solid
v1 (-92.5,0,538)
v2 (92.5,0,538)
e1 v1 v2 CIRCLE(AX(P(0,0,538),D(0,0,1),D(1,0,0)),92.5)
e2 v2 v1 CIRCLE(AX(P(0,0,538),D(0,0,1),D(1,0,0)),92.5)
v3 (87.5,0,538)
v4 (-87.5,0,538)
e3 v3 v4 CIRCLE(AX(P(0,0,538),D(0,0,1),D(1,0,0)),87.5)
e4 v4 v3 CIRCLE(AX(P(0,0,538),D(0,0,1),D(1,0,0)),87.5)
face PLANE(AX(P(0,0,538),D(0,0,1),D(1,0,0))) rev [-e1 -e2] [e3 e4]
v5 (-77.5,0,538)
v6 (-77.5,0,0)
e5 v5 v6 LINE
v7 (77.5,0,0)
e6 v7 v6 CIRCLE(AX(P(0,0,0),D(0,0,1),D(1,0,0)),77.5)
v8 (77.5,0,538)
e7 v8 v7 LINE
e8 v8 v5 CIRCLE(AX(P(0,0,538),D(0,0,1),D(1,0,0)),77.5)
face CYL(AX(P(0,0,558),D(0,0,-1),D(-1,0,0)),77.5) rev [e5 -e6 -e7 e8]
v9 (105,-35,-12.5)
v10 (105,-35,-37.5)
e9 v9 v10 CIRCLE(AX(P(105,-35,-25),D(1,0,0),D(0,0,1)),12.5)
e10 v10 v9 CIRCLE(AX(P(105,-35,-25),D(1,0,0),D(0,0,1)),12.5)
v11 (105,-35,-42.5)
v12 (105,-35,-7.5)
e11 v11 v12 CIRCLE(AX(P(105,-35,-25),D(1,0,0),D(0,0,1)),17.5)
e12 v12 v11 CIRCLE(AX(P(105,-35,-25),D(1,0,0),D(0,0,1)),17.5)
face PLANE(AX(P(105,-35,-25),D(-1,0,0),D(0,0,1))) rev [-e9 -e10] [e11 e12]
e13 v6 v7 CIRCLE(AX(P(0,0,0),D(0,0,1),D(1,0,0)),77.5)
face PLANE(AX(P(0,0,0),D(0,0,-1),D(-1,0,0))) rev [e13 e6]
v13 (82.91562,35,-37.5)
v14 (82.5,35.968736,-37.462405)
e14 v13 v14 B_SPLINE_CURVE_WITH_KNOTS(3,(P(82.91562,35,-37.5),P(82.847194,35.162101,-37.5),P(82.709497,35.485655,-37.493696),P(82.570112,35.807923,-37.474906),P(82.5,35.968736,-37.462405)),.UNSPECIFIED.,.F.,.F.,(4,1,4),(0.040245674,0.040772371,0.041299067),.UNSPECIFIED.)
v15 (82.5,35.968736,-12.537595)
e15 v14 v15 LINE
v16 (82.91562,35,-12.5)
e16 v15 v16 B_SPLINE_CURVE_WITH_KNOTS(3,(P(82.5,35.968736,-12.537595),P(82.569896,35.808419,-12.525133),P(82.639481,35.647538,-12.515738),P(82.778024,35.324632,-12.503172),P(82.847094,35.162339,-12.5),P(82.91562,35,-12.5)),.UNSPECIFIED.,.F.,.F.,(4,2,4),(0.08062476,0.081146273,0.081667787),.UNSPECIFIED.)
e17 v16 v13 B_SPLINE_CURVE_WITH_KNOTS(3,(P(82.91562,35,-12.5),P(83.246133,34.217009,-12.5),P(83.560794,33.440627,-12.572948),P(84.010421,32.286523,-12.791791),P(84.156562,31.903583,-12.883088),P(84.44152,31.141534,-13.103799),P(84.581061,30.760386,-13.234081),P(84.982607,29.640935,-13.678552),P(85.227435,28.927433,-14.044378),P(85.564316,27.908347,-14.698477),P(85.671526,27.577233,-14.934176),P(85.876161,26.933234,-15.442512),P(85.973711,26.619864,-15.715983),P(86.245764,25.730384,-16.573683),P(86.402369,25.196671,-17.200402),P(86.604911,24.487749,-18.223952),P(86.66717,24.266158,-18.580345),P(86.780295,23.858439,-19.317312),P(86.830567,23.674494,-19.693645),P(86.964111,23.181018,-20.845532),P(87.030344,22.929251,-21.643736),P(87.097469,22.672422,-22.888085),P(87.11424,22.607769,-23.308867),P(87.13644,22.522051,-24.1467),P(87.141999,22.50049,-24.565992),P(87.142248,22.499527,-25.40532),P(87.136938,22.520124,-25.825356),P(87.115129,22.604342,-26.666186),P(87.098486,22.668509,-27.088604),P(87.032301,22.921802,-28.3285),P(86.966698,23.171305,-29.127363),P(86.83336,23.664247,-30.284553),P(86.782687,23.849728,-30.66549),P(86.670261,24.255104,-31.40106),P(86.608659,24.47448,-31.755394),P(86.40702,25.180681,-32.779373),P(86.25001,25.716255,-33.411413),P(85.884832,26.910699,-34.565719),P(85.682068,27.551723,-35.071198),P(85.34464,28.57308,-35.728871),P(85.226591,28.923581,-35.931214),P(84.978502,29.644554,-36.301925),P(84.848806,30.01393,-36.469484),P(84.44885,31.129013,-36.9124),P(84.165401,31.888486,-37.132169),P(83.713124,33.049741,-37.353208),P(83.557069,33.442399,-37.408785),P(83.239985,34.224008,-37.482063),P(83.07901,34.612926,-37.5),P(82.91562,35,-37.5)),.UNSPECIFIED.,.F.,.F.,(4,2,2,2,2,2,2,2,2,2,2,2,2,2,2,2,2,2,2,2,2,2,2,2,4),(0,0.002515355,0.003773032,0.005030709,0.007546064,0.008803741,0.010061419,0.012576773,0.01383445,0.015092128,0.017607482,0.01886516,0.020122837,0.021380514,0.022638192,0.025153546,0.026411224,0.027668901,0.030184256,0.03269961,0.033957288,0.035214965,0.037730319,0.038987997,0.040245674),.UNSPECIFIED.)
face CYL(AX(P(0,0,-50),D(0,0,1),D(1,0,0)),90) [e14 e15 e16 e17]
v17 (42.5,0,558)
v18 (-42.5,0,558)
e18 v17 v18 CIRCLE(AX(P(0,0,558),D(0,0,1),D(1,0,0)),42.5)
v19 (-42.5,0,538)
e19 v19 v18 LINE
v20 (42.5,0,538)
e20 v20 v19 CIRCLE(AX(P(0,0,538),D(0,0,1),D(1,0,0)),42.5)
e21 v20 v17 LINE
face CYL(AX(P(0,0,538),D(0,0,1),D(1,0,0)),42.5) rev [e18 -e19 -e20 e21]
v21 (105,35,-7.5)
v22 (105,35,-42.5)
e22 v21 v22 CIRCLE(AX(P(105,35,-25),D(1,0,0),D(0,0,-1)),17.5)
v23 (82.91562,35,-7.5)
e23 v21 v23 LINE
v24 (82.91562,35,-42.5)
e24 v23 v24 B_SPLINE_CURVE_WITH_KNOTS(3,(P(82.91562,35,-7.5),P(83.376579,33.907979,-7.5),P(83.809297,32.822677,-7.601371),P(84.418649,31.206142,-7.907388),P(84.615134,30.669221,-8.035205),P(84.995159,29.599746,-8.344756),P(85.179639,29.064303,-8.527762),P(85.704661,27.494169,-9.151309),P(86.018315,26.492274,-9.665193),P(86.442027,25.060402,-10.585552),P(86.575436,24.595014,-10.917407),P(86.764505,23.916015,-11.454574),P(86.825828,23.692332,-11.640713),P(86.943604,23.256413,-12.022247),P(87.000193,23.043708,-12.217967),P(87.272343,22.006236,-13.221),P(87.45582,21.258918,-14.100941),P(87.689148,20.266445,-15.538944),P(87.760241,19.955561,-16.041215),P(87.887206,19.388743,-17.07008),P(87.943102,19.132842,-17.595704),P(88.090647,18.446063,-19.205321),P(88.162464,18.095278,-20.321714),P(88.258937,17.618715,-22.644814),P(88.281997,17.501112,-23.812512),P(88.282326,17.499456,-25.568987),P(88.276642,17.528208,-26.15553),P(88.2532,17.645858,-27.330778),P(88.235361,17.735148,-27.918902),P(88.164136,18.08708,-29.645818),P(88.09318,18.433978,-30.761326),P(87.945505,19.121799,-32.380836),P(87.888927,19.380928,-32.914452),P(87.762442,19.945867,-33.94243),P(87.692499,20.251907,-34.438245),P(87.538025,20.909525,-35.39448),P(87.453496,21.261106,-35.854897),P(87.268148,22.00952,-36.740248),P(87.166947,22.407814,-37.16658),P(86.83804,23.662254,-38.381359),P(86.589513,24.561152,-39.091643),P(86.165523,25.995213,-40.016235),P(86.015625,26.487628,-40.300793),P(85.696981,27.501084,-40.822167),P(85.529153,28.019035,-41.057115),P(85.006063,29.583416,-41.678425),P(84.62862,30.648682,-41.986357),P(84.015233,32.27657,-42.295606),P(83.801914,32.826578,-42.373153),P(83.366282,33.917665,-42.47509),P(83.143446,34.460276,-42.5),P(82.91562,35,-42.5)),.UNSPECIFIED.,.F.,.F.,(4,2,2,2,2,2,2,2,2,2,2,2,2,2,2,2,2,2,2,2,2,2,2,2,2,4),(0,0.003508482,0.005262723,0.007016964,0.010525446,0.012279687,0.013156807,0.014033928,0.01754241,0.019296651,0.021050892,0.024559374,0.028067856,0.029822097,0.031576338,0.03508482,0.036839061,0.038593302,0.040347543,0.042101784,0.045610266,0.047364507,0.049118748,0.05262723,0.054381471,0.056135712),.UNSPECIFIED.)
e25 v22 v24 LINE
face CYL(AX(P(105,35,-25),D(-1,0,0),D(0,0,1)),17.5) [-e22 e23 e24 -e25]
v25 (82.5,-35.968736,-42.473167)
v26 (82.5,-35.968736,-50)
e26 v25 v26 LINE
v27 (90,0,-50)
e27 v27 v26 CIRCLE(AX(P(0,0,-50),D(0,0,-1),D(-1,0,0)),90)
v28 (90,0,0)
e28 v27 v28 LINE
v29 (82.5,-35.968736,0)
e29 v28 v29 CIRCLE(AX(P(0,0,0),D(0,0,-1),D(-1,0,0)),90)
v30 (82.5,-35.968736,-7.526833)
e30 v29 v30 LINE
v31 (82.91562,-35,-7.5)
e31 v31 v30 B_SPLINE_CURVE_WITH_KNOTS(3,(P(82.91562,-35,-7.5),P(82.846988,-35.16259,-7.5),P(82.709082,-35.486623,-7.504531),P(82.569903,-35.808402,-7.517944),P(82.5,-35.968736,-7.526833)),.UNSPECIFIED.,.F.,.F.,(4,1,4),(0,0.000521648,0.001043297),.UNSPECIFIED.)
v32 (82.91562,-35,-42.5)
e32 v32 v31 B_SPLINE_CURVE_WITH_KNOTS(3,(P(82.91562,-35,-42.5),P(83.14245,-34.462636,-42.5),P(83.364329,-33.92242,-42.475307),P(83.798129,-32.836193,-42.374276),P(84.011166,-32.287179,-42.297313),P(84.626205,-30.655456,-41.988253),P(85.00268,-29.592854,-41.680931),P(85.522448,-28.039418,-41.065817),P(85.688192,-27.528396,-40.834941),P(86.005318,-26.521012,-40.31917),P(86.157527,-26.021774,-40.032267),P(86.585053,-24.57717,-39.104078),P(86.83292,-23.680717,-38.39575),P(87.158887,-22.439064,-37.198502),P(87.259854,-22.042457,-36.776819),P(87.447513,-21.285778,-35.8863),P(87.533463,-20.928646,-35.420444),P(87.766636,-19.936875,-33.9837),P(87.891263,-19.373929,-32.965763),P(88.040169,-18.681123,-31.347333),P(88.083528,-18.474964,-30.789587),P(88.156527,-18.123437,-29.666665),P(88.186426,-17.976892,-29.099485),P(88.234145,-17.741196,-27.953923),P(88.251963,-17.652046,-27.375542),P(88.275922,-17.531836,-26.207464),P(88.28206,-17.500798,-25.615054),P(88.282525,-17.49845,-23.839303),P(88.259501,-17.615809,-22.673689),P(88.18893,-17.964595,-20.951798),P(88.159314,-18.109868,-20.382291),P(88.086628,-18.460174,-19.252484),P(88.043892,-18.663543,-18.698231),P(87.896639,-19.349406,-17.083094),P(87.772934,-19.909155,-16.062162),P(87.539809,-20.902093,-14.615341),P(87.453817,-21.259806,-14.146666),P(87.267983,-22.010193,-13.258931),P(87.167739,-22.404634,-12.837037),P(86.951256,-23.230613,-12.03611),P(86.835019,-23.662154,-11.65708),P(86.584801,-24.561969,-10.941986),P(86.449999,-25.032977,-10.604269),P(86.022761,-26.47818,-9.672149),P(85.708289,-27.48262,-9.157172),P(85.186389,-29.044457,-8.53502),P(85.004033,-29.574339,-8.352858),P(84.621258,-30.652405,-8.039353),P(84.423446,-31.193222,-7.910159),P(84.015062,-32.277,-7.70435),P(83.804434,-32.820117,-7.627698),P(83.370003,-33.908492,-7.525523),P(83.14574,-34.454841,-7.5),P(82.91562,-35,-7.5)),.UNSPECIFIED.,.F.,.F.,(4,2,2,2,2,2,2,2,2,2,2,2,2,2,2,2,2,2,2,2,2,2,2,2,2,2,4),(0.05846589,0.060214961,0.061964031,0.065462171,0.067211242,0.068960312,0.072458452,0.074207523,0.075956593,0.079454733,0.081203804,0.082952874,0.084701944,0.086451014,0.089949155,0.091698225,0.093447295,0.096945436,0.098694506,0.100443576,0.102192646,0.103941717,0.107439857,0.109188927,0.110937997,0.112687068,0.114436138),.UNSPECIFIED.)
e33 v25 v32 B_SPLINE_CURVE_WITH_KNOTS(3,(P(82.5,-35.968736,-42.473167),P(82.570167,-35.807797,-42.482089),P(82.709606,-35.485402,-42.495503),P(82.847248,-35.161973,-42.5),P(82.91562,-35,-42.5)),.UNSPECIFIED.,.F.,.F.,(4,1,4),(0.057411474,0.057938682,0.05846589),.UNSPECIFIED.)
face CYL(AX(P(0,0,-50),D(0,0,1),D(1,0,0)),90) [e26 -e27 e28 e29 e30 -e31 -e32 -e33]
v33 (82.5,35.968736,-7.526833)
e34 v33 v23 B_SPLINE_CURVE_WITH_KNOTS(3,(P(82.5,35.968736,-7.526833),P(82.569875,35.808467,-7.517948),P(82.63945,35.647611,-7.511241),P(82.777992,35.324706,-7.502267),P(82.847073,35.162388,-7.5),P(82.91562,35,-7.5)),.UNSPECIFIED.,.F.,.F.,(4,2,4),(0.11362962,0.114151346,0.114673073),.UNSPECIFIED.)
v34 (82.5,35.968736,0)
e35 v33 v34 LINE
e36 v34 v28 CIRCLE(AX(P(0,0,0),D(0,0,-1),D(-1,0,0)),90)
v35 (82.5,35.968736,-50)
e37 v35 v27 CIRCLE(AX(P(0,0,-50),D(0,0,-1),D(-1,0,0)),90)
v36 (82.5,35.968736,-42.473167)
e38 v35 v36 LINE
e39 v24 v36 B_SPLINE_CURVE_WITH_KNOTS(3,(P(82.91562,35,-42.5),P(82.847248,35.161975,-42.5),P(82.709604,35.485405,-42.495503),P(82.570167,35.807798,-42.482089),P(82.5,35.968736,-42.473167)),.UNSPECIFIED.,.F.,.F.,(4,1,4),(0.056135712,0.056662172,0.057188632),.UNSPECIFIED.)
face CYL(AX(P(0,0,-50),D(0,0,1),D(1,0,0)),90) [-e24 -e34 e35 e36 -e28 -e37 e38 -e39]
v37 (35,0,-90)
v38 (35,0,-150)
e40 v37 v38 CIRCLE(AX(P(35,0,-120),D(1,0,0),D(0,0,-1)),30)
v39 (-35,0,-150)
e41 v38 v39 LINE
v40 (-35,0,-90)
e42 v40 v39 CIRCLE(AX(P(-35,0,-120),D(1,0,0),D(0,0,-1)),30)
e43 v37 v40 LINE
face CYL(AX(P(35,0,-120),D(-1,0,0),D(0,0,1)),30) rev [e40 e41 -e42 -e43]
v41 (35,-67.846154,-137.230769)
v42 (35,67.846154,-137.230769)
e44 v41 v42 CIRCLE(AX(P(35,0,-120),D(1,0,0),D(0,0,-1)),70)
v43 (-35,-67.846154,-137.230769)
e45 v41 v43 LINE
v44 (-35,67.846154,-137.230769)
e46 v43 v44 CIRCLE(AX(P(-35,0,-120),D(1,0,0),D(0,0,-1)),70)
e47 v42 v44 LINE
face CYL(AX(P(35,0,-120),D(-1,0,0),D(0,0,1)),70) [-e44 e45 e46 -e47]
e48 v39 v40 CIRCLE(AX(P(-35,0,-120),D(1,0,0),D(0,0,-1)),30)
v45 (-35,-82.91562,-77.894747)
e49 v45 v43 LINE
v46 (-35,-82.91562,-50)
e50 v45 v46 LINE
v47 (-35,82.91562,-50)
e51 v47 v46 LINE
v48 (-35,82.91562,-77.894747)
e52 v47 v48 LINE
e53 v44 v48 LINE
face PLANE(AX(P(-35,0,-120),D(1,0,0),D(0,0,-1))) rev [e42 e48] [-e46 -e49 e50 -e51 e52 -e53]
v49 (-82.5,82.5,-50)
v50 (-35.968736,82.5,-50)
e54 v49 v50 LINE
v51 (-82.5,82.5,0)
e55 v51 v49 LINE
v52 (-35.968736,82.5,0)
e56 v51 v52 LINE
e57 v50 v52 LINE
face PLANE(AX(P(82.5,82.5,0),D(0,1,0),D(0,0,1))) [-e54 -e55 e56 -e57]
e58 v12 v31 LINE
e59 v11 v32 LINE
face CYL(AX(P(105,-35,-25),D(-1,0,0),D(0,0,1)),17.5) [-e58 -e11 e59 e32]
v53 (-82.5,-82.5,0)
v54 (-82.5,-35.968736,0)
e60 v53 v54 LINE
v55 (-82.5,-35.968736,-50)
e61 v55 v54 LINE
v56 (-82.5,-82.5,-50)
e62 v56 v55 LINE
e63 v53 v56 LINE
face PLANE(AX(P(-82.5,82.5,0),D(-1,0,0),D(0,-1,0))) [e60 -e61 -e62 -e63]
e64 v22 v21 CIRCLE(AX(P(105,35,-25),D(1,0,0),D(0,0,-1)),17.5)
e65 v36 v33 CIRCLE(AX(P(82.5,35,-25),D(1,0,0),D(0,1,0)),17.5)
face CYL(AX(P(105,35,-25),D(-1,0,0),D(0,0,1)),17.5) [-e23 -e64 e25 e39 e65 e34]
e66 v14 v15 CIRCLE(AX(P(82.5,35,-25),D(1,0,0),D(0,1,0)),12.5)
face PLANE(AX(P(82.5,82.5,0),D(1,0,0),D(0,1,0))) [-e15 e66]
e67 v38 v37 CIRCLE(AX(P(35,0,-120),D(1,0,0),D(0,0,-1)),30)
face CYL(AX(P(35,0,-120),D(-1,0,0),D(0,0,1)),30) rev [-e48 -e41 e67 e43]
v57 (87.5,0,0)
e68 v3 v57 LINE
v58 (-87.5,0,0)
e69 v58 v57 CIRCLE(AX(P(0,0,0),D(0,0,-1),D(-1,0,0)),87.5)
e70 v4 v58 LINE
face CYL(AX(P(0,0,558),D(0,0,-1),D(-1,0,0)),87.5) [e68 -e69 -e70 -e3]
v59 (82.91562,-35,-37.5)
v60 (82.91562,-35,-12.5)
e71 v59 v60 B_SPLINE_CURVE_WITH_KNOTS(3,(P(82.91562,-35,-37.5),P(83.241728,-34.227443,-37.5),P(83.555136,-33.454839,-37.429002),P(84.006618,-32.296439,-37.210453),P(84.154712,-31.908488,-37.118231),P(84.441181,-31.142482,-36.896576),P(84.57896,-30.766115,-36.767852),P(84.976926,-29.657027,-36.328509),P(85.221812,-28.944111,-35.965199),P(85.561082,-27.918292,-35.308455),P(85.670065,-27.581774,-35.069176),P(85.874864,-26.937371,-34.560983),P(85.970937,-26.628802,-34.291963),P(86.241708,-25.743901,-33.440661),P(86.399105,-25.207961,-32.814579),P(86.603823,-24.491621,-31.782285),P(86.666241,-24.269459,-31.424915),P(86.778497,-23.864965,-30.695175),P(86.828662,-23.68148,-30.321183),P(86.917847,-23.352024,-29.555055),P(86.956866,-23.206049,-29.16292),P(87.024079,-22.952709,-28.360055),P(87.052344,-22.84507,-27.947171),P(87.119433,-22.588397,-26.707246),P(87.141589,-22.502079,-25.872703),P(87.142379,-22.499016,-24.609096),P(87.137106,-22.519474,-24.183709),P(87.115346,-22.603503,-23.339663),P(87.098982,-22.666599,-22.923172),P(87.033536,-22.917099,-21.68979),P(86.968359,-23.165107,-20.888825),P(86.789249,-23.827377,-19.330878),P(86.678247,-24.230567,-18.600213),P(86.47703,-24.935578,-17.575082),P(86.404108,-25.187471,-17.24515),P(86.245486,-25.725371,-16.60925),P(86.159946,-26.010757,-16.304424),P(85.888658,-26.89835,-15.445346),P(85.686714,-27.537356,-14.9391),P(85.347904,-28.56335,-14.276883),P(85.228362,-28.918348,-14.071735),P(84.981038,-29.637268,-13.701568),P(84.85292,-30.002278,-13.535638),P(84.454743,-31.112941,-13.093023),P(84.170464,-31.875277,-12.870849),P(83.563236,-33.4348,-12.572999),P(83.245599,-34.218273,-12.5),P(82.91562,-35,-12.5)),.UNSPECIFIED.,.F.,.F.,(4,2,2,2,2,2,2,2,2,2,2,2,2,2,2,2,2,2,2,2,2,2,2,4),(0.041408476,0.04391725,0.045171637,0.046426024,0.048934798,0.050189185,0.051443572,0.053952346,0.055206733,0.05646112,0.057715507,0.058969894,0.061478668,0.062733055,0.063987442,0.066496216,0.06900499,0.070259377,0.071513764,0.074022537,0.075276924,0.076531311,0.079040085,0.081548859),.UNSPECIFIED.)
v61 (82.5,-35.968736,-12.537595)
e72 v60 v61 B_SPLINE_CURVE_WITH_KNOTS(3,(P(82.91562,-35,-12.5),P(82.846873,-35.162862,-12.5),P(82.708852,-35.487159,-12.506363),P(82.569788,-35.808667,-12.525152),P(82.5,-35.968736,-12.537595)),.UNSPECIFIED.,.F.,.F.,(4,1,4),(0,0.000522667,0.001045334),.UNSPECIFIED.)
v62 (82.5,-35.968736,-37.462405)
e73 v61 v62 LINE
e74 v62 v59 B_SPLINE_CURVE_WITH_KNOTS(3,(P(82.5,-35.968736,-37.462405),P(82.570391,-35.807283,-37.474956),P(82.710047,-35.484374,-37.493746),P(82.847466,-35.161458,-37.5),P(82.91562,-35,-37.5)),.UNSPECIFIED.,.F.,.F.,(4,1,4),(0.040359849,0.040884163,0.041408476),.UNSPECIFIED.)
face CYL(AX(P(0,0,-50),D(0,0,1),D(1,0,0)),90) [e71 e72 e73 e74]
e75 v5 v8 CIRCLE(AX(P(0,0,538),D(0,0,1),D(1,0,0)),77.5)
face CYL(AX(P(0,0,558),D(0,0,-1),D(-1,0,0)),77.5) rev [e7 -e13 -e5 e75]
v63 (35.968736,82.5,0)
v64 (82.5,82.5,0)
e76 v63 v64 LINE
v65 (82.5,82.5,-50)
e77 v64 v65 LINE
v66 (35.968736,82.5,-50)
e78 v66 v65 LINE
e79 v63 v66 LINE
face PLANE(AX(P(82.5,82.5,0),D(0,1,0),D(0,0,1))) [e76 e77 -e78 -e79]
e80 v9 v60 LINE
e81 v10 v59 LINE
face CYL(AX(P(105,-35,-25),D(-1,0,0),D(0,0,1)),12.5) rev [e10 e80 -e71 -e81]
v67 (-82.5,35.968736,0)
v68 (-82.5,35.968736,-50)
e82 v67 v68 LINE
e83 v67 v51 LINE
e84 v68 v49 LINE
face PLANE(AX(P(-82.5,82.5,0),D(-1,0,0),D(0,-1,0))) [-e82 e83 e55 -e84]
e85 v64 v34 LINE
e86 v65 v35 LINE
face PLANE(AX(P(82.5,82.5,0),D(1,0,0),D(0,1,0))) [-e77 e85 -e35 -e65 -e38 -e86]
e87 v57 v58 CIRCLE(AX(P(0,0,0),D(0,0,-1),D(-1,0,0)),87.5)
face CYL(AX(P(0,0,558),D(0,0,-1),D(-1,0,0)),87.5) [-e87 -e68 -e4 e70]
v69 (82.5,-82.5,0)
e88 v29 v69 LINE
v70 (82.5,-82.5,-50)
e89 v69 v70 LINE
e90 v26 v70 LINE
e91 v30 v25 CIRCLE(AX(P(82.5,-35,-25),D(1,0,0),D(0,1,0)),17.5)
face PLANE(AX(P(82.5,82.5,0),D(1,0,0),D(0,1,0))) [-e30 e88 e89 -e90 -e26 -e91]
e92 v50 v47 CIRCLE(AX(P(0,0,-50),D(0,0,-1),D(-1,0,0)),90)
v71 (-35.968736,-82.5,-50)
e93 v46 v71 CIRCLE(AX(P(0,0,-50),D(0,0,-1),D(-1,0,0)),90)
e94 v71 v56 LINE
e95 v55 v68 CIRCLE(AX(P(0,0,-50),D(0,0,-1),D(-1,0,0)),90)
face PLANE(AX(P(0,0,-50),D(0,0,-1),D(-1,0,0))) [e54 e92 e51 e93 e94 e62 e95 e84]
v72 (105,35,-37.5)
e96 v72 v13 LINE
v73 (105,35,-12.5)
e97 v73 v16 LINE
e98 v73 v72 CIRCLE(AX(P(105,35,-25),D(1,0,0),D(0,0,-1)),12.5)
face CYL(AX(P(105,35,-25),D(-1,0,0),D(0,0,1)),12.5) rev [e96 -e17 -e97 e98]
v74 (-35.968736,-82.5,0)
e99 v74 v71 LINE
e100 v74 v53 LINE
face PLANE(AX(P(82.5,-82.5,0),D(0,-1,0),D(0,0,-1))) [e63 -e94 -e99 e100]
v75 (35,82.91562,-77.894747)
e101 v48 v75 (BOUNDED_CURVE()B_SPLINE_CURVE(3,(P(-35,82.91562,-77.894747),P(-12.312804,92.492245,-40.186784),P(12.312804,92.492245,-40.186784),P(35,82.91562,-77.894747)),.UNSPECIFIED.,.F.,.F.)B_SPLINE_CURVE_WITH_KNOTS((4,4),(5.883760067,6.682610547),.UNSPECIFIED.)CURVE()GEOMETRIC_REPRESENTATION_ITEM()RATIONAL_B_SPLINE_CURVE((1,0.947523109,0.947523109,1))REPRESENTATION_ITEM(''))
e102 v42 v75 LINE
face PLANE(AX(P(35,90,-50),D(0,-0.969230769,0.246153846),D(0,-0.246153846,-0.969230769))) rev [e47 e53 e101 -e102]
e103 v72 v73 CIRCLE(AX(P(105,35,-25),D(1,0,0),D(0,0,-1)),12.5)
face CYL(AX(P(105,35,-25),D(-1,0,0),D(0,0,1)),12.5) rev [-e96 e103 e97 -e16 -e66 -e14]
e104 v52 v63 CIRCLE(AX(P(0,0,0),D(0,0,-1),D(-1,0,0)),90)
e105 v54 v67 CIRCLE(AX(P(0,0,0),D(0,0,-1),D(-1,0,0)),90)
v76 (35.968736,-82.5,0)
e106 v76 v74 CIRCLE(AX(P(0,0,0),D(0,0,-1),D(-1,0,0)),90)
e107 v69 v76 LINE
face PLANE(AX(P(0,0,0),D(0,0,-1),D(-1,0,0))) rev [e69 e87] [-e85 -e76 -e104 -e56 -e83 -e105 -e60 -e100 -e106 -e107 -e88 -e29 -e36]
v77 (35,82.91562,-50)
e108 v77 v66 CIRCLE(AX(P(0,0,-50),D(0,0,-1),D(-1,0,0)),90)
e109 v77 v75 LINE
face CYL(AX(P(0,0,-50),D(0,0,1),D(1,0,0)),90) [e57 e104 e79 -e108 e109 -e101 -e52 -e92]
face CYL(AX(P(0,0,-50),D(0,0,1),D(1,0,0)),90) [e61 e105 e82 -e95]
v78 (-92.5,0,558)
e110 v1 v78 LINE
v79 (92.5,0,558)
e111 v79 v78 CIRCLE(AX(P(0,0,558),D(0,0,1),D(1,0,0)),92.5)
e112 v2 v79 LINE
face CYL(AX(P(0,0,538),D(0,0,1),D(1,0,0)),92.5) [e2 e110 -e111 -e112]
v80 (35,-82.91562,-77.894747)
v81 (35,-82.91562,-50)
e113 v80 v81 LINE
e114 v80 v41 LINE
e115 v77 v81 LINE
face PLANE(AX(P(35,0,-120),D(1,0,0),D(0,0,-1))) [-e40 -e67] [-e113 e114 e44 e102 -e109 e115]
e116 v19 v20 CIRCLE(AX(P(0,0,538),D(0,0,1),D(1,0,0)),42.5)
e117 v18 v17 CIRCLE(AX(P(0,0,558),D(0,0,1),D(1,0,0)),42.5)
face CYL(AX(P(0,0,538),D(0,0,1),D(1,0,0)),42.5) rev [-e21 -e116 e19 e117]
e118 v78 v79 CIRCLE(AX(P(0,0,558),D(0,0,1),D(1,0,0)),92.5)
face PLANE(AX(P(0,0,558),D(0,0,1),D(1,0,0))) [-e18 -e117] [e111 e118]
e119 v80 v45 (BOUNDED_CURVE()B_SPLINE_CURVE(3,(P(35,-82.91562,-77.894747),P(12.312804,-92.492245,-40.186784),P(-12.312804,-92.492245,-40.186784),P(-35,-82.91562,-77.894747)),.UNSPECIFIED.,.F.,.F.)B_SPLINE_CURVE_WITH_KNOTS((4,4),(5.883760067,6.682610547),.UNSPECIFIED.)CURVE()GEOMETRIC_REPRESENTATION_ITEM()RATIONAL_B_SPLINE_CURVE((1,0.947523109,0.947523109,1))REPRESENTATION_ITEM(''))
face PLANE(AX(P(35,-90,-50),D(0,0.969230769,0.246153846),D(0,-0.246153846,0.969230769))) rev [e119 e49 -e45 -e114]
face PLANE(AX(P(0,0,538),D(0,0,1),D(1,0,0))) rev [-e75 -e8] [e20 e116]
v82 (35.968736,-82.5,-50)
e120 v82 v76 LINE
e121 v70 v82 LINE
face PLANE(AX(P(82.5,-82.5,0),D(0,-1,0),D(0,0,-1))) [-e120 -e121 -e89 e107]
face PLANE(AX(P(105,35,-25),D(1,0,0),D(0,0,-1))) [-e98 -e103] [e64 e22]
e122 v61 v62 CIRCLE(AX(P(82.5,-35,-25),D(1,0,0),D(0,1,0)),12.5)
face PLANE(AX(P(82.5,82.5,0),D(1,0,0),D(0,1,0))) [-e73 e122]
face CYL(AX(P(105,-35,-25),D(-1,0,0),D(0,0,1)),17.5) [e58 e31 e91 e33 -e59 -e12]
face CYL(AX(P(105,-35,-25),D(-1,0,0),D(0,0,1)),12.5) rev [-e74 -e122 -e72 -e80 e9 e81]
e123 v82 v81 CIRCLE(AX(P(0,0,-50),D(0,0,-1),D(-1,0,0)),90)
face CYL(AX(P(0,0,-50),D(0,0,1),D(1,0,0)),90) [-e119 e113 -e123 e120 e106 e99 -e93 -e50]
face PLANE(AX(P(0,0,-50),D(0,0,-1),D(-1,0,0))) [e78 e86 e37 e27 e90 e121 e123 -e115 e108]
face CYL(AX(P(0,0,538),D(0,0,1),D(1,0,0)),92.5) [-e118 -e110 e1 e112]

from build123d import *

# Parameters (mm, degrees)
SKETCH_1_R          = 87.5
SKETCH_1_R_2        = 77.5
EXTRUDE_1_DEPTH     = 558
SKETCH_4_R          = 90
EXTRUDE_2_DEPTH     = 50
SKETCH_5_R          = 30
EXTRUDE_3_DEPTH     = 35
SKETCH_6_OUTSIDE_W  = 340.026
SKETCH_6_OUTSIDE_H  = 340.026
SKETCH_6_OUTSIDE_R  = 90
CUT_EXTRUDE_2_DEPTH = 622.179523165
SKETCH_7_R          = 17.5
SKETCH_7_R_2        = 12.5
EXTRUDE_4_DEPTH     = 105
SKETCH_8_R          = 92.5
SKETCH_8_R_2        = 42.5
EXTRUDE_5_DEPTH     = 20
SKETCH_9_W          = 165
SKETCH_9_H          = 165
EXTRUDE_6_DEPTH     = 50


with BuildPart() as part:
    # 草图1 → 凸台-拉伸1 (new body)
    with BuildSketch(Plane.XY):
        Circle(SKETCH_1_R)
        Circle(SKETCH_1_R_2, mode=Mode.SUBTRACT)
    extrude(amount=EXTRUDE_1_DEPTH)

    # 草图4 → 凸台-拉伸2 (add)
    with BuildSketch(Plane(origin=(0, 0, 0), x_dir=(-1, 0, 0), z_dir=(0, 0, -1))):
        Circle(SKETCH_4_R)
    extrude(amount=EXTRUDE_2_DEPTH)

    # 草图5 → 凸台-拉伸3 (add, symmetric)
    with BuildSketch(Plane(origin=(0, 0, 0), x_dir=(0, 0, -1), z_dir=(1, 0, 0))):
        with BuildLine():
            Line((50, 90), (137.230769231, 67.846153846))
            ThreePointArc((137.230769231, 67.846153846), (190, 0), (137.230769231, -67.846153846))
            Line((137.230769231, -67.846153846), (50, -90))
            Line((50, -90), (50, 90))
        make_face()
        with Locations((120, 0)):
            Circle(SKETCH_5_R, mode=Mode.SUBTRACT)
    extrude(amount=EXTRUDE_3_DEPTH, both=True)

    # 草图6 outside → 切除-拉伸2 (cut, through all)
    with BuildSketch(Plane(origin=(0, 0, -50), x_dir=(-1, 0, 0), z_dir=(0, 0, -1))):
        Rectangle(SKETCH_6_OUTSIDE_W, SKETCH_6_OUTSIDE_H)
        with Locations(Location((0, 0, 0), (0, 0, 247.114619524))):
            Circle(SKETCH_6_OUTSIDE_R, mode=Mode.SUBTRACT)
    extrude(amount=CUT_EXTRUDE_2_DEPTH, mode=Mode.SUBTRACT)

    # 草图7 → 凸台-拉伸4 (add)
    # profile 1 of 2: a face of its own
    with BuildSketch(Plane(origin=(0, 0, 0), x_dir=(0, 0, -1), z_dir=(1, 0, 0))):
        with Locations(Location((25, 35, 0), (0, 0, 180))):
            Circle(SKETCH_7_R)
        with Locations(Location((25, 35, 0), (0, 0, 180))):
            Circle(SKETCH_7_R_2, mode=Mode.SUBTRACT)
    # profile 2 of 2: a face of its own
    with BuildSketch(Plane(origin=(0, 0, 0), x_dir=(0, 0, -1), z_dir=(1, 0, 0))):
        with Locations(Location((25, -35, 0), (0, 0, 180))):
            Circle(SKETCH_7_R)
        with Locations(Location((25, -35, 0), (0, 0, 180))):
            Circle(SKETCH_7_R_2, mode=Mode.SUBTRACT)
    extrude(amount=EXTRUDE_4_DEPTH)

    # 草图8 → 凸台-拉伸5 (add)
    with BuildSketch(Plane.XY.offset(558)):
        Circle(SKETCH_8_R)
        Circle(SKETCH_8_R_2, mode=Mode.SUBTRACT)
    extrude(amount=-EXTRUDE_5_DEPTH)

    # 草图9 → 凸台-拉伸6 (add)
    with BuildSketch(Plane(origin=(0, 0, -50), x_dir=(-1, 0, 0), z_dir=(0, 0, -1))):
        Rectangle(SKETCH_9_W, SKETCH_9_H)
    extrude(amount=-EXTRUDE_6_DEPTH)


solid = part.part
